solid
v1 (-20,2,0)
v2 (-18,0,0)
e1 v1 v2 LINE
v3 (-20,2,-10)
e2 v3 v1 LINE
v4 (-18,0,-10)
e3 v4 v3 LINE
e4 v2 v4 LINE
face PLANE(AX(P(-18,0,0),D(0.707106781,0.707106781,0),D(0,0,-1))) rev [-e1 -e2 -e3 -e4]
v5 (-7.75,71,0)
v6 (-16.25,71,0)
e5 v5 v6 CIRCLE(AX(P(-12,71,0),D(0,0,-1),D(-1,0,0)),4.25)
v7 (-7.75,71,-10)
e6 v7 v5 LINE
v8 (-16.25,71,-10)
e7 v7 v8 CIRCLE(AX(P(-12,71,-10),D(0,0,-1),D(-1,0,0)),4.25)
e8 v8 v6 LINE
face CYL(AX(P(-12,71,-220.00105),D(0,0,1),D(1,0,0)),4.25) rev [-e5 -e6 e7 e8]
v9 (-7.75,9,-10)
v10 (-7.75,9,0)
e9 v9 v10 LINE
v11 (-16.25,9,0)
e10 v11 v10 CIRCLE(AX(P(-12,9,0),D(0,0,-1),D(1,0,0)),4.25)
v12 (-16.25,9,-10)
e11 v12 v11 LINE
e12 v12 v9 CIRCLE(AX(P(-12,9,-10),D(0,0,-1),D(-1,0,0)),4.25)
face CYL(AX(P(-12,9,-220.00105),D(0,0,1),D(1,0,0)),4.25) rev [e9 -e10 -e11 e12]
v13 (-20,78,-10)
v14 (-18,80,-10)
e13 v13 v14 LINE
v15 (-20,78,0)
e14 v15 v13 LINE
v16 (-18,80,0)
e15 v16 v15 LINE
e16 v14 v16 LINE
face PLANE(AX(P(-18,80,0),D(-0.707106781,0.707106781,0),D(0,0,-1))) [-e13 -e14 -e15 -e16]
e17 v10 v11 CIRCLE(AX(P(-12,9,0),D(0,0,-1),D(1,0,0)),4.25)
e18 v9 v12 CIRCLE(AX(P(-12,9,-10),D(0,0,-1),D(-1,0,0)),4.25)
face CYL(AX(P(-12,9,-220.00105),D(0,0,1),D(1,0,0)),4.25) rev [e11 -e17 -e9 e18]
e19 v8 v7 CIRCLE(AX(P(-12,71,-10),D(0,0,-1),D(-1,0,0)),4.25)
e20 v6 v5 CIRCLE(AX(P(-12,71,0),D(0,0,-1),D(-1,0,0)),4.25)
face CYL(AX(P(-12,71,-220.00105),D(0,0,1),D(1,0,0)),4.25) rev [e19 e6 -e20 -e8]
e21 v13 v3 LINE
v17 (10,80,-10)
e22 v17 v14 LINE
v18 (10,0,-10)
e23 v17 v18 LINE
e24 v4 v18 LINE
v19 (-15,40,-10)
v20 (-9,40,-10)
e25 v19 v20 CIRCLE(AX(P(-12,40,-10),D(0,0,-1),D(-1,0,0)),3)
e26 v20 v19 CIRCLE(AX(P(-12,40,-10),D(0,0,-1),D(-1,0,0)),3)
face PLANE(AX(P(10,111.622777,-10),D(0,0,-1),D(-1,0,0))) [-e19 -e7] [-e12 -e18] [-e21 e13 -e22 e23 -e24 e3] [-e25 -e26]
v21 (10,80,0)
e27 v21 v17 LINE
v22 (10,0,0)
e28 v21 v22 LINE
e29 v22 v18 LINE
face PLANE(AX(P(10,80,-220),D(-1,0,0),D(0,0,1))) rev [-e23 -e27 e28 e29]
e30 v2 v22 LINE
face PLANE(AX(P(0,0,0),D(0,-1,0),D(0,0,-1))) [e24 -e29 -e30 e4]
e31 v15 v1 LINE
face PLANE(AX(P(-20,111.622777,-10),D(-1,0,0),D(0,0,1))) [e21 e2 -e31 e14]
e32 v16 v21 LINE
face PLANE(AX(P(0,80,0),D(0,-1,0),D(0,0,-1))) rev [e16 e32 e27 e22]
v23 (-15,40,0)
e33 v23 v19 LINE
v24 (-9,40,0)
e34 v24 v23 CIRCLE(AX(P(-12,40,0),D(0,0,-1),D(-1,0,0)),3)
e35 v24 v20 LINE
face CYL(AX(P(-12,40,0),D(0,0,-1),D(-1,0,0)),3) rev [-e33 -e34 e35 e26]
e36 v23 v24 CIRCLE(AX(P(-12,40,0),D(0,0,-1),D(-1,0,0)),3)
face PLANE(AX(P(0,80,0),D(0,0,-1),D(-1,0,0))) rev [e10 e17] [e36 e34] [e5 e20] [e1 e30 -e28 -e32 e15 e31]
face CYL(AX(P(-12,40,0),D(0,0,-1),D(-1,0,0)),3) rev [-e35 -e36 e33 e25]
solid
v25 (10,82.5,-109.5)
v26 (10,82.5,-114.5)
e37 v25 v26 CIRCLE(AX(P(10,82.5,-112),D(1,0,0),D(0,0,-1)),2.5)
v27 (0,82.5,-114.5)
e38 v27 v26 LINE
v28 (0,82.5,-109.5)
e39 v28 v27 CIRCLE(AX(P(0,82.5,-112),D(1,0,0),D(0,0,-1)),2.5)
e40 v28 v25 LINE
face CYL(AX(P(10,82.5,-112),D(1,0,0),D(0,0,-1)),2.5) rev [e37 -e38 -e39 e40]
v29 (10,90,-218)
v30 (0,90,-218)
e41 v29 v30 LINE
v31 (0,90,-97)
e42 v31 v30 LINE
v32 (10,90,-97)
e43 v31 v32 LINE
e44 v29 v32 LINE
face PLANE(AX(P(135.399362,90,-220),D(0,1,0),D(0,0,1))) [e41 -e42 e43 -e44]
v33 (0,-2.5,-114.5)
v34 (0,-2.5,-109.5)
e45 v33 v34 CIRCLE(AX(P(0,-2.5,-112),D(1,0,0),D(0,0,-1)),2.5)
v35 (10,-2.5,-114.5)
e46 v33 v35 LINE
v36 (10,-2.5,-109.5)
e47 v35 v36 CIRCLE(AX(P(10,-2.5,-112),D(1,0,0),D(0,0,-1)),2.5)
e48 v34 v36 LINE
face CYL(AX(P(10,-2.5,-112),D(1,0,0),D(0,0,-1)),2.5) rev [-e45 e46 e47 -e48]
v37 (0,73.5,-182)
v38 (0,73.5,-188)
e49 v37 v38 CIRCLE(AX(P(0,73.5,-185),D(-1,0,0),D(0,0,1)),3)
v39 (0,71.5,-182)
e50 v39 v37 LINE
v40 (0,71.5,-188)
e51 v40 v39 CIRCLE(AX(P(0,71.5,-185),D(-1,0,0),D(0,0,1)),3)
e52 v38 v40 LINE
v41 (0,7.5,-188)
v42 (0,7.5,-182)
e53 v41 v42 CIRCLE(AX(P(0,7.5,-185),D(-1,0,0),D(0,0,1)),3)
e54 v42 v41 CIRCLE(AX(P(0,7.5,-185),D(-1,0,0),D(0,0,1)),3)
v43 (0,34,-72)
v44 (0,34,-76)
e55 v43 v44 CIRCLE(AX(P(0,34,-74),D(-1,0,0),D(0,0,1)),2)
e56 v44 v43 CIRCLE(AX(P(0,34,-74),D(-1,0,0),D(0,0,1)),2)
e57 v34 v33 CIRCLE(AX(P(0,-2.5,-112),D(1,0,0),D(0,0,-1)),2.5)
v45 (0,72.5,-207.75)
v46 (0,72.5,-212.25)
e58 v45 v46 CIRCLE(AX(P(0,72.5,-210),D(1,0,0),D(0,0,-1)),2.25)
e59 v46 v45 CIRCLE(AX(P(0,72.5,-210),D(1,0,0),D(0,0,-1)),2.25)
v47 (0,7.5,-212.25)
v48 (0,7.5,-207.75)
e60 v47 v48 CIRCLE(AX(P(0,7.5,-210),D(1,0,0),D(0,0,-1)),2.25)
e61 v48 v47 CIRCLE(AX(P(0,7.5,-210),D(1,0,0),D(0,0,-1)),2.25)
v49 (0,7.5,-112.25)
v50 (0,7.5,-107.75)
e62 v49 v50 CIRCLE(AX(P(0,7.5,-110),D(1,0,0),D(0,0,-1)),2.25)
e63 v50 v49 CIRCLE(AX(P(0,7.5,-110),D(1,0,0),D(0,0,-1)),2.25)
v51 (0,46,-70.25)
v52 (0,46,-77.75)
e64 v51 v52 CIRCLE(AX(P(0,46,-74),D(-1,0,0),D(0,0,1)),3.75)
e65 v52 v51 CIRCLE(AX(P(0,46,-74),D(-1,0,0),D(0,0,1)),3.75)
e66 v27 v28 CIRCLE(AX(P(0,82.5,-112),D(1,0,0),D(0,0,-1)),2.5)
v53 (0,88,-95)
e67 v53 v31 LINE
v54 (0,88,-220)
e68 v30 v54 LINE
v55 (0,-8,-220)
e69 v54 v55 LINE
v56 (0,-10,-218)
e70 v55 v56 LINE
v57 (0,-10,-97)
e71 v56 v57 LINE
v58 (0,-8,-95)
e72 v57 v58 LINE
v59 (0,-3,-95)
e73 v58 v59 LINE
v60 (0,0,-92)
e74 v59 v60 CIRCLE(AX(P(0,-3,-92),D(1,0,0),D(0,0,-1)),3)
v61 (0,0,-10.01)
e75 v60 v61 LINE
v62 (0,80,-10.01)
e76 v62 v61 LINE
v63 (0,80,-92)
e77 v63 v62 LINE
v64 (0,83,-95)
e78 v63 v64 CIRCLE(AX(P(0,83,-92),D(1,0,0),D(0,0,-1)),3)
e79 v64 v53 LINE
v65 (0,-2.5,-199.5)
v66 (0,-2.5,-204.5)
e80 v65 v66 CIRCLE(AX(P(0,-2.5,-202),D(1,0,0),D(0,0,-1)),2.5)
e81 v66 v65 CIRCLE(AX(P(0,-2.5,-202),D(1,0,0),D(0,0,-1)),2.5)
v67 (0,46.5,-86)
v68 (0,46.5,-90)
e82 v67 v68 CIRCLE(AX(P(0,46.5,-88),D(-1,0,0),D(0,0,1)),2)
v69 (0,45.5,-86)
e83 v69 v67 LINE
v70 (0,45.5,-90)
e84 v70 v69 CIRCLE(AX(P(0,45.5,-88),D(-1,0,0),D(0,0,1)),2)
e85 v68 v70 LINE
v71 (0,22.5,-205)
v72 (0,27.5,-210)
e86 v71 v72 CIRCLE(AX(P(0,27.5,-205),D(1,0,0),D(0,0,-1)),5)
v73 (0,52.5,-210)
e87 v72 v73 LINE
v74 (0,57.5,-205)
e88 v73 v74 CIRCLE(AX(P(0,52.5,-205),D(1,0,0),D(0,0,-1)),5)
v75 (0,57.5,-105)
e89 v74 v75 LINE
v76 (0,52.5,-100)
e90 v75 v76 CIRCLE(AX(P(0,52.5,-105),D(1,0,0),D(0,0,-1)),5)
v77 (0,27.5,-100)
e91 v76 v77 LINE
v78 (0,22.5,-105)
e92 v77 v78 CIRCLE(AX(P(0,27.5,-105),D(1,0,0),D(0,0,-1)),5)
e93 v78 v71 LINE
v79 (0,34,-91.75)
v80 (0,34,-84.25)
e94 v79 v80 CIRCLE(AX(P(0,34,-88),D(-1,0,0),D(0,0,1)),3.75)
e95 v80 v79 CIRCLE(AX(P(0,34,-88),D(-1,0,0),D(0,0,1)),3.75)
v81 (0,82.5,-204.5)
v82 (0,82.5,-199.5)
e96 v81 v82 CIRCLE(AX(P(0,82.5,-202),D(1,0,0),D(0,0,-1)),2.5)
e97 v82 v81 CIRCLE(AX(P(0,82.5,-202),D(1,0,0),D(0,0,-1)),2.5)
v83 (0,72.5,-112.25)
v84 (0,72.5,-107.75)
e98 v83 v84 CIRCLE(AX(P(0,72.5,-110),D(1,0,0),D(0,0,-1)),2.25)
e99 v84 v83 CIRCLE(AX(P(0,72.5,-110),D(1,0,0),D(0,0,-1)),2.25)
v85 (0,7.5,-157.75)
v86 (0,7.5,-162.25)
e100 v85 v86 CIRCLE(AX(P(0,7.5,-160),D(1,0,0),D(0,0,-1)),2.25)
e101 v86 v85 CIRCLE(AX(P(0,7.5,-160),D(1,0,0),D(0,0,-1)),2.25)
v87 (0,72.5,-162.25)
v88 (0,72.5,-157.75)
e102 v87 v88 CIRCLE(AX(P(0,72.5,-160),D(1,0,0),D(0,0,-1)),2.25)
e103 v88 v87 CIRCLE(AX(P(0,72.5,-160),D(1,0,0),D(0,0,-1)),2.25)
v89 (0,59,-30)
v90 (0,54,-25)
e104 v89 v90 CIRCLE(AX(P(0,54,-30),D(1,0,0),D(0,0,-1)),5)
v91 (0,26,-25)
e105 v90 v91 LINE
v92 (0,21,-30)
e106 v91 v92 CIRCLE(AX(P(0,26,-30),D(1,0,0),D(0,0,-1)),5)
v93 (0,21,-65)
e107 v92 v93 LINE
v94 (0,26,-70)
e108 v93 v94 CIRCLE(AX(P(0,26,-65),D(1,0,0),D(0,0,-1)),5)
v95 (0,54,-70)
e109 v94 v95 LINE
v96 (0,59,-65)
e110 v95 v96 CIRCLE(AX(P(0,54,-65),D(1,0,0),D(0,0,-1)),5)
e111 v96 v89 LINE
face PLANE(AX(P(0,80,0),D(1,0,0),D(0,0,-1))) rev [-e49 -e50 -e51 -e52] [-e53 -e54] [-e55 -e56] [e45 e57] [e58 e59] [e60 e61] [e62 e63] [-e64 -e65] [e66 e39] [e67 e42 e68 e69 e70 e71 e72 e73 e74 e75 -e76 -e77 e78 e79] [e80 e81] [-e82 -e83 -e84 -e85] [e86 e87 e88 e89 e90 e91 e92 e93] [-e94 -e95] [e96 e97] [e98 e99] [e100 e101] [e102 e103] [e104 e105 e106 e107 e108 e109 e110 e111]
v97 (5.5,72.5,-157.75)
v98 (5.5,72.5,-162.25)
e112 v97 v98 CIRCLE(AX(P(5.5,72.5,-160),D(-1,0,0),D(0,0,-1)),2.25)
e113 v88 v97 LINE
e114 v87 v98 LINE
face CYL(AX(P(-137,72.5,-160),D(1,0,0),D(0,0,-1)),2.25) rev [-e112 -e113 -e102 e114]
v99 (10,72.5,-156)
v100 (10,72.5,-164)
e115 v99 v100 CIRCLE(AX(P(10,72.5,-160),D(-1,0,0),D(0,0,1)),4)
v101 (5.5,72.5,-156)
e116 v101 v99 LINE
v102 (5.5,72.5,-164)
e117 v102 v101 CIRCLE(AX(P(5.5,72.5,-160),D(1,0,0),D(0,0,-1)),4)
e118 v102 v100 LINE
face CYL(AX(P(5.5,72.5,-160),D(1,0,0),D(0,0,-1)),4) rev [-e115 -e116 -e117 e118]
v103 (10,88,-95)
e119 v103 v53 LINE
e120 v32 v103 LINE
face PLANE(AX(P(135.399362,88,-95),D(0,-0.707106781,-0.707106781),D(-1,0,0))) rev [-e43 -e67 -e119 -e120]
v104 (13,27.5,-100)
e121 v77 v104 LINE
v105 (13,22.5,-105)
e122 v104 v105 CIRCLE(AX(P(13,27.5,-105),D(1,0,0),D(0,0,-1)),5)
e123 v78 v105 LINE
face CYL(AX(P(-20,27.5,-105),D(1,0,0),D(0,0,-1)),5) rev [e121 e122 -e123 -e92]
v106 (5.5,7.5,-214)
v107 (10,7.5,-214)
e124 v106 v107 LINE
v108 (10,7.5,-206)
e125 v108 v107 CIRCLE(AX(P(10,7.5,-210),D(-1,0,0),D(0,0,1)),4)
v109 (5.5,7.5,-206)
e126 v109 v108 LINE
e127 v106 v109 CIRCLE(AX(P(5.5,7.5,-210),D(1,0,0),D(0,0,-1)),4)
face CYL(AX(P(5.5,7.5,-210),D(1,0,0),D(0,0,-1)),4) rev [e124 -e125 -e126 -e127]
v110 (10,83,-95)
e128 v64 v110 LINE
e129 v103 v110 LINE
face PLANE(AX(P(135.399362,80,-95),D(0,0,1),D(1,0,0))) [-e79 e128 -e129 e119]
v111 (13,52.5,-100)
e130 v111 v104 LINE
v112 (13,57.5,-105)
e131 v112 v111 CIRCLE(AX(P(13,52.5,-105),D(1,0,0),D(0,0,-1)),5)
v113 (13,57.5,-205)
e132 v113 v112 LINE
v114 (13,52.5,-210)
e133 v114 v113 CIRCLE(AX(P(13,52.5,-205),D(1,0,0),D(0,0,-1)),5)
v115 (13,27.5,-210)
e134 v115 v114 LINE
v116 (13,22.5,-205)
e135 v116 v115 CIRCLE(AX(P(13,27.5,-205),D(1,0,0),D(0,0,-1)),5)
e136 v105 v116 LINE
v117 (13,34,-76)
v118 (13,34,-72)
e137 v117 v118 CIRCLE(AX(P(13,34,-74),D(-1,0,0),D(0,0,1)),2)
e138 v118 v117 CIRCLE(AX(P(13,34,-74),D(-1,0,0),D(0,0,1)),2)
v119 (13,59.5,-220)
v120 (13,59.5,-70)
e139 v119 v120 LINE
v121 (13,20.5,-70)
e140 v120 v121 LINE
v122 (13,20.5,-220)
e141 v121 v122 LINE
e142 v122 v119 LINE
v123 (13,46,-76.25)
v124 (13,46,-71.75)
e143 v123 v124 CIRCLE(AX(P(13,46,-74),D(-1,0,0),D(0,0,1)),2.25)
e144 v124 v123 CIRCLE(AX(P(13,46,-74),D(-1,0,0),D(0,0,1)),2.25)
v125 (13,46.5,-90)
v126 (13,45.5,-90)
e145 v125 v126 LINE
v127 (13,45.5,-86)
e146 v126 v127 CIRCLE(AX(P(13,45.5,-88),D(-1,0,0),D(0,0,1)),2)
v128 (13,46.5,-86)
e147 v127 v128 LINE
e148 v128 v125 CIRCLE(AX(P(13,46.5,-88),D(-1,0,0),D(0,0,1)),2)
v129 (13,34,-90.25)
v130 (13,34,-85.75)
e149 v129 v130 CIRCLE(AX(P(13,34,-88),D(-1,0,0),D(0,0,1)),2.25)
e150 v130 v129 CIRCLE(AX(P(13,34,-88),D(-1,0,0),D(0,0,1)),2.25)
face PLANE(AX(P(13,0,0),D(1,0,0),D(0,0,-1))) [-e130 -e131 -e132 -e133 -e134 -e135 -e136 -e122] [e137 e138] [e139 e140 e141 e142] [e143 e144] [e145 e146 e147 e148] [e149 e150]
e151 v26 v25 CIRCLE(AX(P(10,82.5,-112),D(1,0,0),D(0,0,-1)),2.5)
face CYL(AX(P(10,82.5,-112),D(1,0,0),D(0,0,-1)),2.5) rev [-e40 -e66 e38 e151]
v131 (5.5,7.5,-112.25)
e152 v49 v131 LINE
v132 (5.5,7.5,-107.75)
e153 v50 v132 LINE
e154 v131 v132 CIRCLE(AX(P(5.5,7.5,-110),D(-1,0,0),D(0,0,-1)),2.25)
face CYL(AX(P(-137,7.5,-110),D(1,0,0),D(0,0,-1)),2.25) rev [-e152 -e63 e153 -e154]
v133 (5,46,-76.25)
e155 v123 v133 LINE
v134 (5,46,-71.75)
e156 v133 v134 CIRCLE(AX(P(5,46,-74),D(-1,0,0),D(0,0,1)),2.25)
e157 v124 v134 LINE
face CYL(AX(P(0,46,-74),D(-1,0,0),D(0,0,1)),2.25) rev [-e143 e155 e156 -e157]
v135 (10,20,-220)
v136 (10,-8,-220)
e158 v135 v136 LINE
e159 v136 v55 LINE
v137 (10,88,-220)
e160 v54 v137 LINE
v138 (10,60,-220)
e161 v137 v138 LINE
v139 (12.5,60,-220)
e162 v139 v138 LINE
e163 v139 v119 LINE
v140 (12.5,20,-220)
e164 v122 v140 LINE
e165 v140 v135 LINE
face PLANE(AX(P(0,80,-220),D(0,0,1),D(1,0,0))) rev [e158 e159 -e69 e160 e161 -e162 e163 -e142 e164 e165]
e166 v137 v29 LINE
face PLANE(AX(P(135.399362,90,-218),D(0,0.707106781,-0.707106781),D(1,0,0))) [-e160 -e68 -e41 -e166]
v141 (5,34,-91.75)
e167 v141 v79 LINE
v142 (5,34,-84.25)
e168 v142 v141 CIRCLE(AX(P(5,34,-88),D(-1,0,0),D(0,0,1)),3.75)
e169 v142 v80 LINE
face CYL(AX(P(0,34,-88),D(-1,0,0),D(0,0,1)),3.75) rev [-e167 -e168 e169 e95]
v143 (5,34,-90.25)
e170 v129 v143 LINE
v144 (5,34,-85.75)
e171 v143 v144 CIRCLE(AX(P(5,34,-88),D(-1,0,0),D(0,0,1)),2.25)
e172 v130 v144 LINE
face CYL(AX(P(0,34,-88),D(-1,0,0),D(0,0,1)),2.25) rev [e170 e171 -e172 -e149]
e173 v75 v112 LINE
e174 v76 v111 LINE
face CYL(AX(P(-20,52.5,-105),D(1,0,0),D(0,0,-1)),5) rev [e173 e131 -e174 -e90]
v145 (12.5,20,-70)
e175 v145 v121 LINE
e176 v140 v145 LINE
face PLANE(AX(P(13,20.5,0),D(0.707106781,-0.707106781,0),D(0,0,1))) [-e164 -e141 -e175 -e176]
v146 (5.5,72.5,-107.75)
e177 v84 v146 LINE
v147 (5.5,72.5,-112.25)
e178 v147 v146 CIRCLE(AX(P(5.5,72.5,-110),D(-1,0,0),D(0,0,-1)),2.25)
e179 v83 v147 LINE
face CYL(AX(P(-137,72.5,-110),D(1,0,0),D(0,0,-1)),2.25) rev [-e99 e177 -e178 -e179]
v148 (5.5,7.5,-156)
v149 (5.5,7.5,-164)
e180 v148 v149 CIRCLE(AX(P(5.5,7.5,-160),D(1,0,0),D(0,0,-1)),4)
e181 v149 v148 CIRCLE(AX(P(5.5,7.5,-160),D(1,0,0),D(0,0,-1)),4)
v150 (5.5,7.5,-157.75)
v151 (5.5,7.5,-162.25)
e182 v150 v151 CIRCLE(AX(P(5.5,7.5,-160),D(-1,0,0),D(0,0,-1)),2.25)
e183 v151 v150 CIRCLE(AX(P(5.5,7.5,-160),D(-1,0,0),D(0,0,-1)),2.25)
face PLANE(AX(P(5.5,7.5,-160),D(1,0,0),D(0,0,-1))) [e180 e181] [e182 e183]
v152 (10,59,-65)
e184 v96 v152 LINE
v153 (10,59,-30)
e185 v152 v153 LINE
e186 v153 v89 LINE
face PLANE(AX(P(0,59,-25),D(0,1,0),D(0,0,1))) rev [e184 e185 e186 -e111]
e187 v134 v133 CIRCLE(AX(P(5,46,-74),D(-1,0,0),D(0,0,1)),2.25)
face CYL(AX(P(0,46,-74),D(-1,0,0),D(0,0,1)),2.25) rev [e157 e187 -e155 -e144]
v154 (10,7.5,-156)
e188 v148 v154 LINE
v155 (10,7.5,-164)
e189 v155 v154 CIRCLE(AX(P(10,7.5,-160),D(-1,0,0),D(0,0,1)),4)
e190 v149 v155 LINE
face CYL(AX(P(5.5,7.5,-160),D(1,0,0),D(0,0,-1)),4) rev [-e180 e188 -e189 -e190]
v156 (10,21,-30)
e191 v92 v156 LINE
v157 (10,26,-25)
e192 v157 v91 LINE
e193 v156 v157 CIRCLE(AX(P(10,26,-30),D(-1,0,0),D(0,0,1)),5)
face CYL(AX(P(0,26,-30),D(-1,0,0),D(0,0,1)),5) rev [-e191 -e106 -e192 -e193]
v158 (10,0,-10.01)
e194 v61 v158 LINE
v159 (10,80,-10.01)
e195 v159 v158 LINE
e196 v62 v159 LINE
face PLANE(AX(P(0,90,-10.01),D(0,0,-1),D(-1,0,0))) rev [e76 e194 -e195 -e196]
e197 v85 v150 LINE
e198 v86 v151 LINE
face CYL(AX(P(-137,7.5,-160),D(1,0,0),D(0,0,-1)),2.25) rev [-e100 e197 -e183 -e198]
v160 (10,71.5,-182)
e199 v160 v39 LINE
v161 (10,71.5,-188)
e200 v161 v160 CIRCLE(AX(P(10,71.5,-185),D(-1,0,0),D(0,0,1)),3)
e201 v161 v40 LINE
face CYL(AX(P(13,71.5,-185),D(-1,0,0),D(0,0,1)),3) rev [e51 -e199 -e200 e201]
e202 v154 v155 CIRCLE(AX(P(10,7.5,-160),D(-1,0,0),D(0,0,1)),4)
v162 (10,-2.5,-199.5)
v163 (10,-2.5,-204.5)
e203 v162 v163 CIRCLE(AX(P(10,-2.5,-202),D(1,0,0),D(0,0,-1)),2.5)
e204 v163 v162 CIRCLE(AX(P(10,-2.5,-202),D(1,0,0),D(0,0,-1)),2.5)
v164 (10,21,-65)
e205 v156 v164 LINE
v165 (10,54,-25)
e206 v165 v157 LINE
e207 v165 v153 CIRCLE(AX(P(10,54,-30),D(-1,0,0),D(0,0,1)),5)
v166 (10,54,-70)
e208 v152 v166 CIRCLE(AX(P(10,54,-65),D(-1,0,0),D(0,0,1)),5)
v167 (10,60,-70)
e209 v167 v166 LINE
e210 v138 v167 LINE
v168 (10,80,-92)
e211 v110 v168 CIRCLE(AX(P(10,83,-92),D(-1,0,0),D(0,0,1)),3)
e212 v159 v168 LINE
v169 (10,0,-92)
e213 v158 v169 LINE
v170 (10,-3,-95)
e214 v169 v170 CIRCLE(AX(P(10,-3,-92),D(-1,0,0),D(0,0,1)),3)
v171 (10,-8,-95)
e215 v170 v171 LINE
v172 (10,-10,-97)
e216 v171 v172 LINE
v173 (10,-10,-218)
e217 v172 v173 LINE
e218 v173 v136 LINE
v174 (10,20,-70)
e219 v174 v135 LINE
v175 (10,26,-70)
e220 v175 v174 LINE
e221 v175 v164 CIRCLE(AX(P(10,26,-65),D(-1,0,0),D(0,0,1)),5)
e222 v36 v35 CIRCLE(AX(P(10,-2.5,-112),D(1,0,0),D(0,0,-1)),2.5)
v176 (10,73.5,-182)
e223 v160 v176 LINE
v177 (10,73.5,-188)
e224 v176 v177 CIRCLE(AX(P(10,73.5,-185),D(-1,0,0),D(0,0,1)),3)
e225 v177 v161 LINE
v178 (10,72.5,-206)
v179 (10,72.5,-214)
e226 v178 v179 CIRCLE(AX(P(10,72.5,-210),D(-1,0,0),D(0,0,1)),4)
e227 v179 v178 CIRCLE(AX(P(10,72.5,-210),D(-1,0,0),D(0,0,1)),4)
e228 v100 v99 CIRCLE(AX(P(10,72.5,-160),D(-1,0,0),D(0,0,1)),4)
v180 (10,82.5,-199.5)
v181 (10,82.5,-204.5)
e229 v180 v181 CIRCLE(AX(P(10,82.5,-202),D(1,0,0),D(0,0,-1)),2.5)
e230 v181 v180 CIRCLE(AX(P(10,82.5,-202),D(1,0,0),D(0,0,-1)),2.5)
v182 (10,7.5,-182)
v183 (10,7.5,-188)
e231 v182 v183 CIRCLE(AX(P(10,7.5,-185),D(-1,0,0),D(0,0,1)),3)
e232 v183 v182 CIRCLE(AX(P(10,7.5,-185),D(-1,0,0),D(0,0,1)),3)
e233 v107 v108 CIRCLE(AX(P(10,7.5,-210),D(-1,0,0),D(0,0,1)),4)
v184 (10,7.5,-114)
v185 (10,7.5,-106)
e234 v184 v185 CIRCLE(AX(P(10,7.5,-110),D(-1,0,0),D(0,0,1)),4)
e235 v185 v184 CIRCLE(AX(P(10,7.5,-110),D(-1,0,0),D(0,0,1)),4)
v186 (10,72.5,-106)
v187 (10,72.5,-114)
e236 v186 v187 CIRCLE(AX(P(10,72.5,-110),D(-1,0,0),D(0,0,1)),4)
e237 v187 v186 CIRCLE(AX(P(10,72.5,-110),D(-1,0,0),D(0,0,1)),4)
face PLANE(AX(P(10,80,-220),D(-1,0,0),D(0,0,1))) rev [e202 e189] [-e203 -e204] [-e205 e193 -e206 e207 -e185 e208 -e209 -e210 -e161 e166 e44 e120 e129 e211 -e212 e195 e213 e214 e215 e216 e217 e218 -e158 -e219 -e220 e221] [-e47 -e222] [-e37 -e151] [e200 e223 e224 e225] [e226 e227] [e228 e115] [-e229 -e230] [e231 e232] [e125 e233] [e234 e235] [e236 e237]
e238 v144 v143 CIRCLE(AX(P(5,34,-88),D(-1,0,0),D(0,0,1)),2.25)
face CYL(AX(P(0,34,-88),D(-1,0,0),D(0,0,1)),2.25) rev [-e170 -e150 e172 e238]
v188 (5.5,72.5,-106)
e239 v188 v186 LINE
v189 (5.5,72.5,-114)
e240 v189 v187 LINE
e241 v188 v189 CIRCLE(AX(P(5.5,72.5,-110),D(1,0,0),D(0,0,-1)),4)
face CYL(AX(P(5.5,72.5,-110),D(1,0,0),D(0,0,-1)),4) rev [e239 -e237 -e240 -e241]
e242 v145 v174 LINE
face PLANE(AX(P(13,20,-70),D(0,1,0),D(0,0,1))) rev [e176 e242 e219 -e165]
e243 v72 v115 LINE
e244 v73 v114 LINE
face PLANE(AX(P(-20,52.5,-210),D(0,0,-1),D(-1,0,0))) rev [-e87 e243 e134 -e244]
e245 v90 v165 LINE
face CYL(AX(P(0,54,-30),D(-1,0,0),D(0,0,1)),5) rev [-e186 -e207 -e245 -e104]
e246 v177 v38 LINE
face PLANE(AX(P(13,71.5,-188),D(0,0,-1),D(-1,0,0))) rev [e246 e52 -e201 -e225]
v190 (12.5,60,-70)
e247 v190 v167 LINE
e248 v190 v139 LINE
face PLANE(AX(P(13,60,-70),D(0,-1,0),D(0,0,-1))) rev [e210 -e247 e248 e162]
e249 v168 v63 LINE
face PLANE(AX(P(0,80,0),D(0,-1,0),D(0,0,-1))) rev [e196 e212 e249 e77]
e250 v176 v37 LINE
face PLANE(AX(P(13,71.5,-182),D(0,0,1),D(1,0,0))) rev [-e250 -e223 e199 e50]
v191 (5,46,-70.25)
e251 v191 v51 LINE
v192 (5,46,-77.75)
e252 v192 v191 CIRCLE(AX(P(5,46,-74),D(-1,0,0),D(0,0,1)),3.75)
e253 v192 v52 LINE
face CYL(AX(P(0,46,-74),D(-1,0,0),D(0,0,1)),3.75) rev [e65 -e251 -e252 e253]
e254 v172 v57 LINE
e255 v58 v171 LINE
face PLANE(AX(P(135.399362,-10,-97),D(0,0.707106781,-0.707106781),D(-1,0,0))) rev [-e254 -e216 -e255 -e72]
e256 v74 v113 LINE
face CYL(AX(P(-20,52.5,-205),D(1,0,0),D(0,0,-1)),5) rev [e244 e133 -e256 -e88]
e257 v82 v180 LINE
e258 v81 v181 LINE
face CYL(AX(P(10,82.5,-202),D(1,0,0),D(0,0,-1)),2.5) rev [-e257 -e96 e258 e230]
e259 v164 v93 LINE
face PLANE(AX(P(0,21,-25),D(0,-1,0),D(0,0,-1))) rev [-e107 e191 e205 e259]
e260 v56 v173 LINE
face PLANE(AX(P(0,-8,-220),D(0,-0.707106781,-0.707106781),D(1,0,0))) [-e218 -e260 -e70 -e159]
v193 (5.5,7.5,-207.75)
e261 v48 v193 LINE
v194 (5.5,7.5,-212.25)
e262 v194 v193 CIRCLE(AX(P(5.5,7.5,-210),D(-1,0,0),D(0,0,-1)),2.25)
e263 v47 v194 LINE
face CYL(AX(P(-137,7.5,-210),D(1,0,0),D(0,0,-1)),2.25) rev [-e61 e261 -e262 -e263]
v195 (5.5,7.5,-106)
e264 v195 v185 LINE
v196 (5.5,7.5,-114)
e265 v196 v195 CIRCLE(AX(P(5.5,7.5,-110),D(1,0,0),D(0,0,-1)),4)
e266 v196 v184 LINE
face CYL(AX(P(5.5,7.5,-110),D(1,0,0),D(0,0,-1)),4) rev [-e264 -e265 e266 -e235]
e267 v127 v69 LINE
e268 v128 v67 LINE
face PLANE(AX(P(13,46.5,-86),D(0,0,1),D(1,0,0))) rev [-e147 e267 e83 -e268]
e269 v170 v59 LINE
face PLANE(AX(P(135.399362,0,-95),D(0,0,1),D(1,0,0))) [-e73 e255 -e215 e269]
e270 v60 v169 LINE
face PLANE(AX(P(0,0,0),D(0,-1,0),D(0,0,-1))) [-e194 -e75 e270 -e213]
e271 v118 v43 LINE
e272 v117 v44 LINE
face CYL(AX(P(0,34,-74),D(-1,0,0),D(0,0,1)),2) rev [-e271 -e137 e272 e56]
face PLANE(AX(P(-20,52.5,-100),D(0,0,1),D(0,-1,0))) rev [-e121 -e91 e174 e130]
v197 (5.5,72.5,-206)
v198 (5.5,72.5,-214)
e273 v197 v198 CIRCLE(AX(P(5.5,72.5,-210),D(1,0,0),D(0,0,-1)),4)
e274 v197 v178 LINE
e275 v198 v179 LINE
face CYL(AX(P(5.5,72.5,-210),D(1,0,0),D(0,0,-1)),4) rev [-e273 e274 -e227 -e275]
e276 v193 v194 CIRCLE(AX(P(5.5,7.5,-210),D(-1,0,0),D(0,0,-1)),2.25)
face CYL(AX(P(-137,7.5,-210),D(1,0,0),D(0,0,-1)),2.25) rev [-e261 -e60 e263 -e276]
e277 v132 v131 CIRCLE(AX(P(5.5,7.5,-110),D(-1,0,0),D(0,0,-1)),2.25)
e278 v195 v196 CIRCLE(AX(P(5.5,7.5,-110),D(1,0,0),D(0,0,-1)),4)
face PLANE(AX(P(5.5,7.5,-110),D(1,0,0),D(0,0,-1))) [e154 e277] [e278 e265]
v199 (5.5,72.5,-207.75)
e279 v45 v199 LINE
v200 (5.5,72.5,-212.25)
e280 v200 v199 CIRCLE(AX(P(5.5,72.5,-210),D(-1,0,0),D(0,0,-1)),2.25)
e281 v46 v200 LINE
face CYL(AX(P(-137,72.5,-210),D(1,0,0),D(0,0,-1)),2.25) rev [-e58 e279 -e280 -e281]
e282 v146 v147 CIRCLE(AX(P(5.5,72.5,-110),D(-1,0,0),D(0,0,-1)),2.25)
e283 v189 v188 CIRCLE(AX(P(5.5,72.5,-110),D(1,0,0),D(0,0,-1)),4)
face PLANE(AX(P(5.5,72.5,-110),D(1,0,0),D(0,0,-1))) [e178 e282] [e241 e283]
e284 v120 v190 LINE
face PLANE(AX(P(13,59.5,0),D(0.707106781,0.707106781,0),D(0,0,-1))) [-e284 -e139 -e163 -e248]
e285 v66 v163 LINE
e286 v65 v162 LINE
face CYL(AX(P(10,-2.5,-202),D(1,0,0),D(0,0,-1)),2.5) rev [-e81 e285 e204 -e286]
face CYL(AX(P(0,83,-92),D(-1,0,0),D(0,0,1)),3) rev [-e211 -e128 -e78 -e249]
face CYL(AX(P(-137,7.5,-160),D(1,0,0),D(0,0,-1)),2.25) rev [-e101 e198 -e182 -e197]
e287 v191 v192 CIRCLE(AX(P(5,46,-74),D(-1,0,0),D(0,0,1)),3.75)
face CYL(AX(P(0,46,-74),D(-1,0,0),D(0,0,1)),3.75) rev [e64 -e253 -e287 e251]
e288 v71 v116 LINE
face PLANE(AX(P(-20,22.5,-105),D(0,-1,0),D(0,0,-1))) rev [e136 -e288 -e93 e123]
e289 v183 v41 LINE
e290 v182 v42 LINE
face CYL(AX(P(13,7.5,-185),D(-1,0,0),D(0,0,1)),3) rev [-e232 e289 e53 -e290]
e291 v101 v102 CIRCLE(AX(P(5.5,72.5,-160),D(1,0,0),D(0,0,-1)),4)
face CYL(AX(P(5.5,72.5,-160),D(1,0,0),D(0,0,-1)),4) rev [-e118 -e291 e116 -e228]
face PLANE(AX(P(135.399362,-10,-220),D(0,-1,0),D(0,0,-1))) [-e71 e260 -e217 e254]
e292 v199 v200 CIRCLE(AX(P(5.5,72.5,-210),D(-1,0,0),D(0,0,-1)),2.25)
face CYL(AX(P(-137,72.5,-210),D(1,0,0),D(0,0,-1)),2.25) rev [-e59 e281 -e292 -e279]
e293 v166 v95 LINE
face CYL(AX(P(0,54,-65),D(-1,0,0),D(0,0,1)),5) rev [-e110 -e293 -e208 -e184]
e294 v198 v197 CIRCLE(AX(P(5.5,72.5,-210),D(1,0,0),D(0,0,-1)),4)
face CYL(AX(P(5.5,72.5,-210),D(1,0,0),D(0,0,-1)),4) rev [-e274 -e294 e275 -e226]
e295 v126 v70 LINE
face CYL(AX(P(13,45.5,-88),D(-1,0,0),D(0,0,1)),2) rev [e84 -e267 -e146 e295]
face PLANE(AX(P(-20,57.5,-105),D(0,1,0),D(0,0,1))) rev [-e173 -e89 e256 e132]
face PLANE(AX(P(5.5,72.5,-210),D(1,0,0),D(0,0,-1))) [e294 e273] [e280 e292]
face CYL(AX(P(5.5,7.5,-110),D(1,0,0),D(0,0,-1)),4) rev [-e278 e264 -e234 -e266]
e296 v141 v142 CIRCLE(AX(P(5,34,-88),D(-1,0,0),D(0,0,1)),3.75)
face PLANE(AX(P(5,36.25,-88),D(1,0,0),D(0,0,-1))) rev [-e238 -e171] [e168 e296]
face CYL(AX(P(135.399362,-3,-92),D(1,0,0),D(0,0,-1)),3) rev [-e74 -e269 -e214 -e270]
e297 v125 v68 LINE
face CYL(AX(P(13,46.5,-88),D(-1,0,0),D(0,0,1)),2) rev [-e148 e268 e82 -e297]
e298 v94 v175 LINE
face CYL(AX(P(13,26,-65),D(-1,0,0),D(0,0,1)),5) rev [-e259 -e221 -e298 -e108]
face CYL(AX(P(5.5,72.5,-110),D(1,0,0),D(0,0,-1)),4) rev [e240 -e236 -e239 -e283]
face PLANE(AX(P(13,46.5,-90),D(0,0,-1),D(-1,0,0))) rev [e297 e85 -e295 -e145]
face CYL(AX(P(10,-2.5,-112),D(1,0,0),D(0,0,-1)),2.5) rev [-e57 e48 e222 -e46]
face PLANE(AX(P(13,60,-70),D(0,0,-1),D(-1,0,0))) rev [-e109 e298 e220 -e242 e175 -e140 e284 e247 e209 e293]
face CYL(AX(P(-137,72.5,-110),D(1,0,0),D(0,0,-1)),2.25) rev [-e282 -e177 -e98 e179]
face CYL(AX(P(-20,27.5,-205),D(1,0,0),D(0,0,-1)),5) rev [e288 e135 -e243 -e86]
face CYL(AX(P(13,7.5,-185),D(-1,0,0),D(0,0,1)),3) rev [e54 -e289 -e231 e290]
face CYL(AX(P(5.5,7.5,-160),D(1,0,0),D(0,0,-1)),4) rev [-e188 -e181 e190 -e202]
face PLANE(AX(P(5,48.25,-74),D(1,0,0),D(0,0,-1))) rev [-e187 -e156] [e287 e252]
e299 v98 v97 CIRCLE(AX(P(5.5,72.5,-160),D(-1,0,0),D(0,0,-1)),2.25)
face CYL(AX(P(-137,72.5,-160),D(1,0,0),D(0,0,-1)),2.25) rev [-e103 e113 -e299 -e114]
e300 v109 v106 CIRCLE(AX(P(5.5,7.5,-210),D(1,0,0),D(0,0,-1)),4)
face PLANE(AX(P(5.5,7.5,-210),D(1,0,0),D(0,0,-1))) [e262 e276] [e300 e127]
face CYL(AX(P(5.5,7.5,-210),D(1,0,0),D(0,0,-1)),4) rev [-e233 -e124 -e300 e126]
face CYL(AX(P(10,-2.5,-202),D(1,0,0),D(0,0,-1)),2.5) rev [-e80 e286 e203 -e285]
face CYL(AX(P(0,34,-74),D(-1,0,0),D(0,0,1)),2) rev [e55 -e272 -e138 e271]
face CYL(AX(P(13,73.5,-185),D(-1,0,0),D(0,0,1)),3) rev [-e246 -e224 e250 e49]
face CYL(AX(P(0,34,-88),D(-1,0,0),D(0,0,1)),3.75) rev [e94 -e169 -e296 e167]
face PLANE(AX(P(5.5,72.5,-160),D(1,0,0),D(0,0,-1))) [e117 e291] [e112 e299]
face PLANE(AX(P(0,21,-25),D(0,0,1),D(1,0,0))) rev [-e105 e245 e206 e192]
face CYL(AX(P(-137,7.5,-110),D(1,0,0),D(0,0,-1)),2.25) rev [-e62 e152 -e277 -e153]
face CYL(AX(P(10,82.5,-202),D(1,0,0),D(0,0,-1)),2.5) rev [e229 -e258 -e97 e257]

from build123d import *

# Parameters (mm, degrees)
BOSS_EXTRUDE1_DEPTH                                  = 80
CHAMFER1_SIZE                                        = 10
SKETCH2_W                                            = 30
SKETCH2_H                                            = 10
BOSS_EXTRUDE2_DEPTH                                  = 80
SKETCH3_W                                            = 10
SKETCH3_H                                            = 8
CUT_EXTRUDE1_DEPTH                                   = 96
SKETCH4_W                                            = 150
SKETCH4_H                                            = 40
BOSS_EXTRUDE3_DEPTH                                  = 3
CUT_EXTRUDE2_REACH                                   = 236.947
SKETCH5_R                                            = 4.25
CHAMFER5_SIZE                                        = 0.5
SKETCH13_R                                           = 2.25
CUT_EXTRUDE7_DEPTH                                   = 150
SKETCH14_R                                           = 4
CUT_EXTRUDE8_DEPTH                                   = 7.5
SKETCH15_W                                           = 125
SKETCH15_H                                           = 10
BOSS_EXTRUDE5_DEPTH                                  = 10
SKETCH9_R                                            = 1
CUT_EXTRUDE4_DEPTH                                   = 25
M6_TAPPED_HOLE1_D                                    = 5
SKETCH18_W                                           = 45
SKETCH18_H                                           = 38
CUT_EXTRUDE10_DEPTH                                  = 10
FILLET2_R                                            = 5
FILLET3_R                                            = 3
CHAMFER6_SIZE                                        = 2
HOLE_SIZE_PER_SOCKET_HEAD_CAP_SCREW_TYPE_D           = 4.5
HOLE_SIZE_PER_SOCKET_HEAD_CAP_SCREW_TYPE_CBORE_D     = 7.5
HOLE_SIZE_PER_SOCKET_HEAD_CAP_SCREW_TYPE_CBORE_DEPTH = 5
F_4_0_4_DIAMETER_HOLE1_D                             = 4
CUT_EXTRUDE11_DEPTH                                  = 240.977082239
SKETCH24_R                                           = 3
CUT_EXTRUDE12_DEPTH                                  = 239.537208838
SKETCH25_W                                           = 10
SKETCH25_H                                           = 0.01
CUT_EXTRUDE13_DEPTH                                  = 239.537208838
SKETCH26_R                                           = 3
CUT_EXTRUDE14_DEPTH                                  = 230.346898824
CUT_EXTRUDE15_DEPTH                                  = 239.537208838


with BuildPart() as part:
    # Sketch1 → Boss-Extrude1 (new body)
    with BuildSketch(Plane(origin=(0, 0, 0), x_dir=(1, 0, 0), z_dir=(0, 1, 0))):
        Polygon((0, 0), (20, 0), (20, 8), (10, 8), (10, 220), (0, 220), align=None)
    extrude(amount=BOSS_EXTRUDE1_DEPTH)

    # Chamfer1
    chamfer1_edges = [part.edges().sort_by_distance(p)[0] for p in [
        (20, 80, -4),
        (20, 0, -4),
    ]]
    chamfer(chamfer1_edges, length=CHAMFER1_SIZE)

    # Sketch2 → Boss-Extrude2 (add)
    with BuildSketch(Plane.XZ):
        with Locations((-5, -5)):
            Rectangle(SKETCH2_W, SKETCH2_H)
    extrude(amount=-BOSS_EXTRUDE2_DEPTH)

    # Sketch3 → Cut-Extrude1 (cut)
    with BuildSketch(Plane.XZ):
        with Locations((15, -4)):
            Rectangle(SKETCH3_W, SKETCH3_H)
    extrude(amount=-CUT_EXTRUDE1_DEPTH, mode=Mode.SUBTRACT)

    # Sketch4 → Boss-Extrude3 (add)
    with BuildSketch(Plane(origin=(10, 0, 0), x_dir=(0, 0, -1), z_dir=(1, 0, 0))):
        with Locations((145, 40)):
            Rectangle(SKETCH4_W, SKETCH4_H)
    extrude(amount=BOSS_EXTRUDE3_DEPTH)

    # Sketch5 → Cut-Extrude2 (cut, up to next)
    with BuildSketch(Plane(origin=(0, 0, 0), x_dir=(-1, 0, 0), z_dir=(0, 0, -1)), mode=Mode.PRIVATE) as cut_extrude2_sk1:
        with Locations((12, 71)):
            Circle(SKETCH5_R)
    cut_extrude2_tool1 = extrude(cut_extrude2_sk1.sketch, amount=CUT_EXTRUDE2_REACH, mode=Mode.PRIVATE) & part.part
    # Sketch5 → Cut-Extrude2 (cut, up to next)
    with BuildSketch(Plane(origin=(0, 0, 0), x_dir=(-1, 0, 0), z_dir=(0, 0, -1)), mode=Mode.PRIVATE) as cut_extrude2_sk2:
        with Locations(Location((12, 9, 0), (0, 0, 180))):
            Circle(SKETCH5_R)
    cut_extrude2_tool2 = extrude(cut_extrude2_sk2.sketch, amount=CUT_EXTRUDE2_REACH, mode=Mode.PRIVATE) & part.part
    add(cut_extrude2_tool1.solids().sort_by_distance((-12, 71, 0))[0], mode=Mode.SUBTRACT)
    add(cut_extrude2_tool2.solids().sort_by_distance((-12, 9, 0))[0], mode=Mode.SUBTRACT)

    # Chamfer5
    chamfer5_edges = [part.edges().sort_by_distance(p)[0] for p in [
        (13, 60, -145),
        (13, 20, -145),
    ]]
    chamfer(chamfer5_edges, length=CHAMFER5_SIZE)

    # Sketch13 → Cut-Extrude7 (cut)
    with BuildSketch(Plane(origin=(13, 0, 0), x_dir=(0, 0, -1), z_dir=(1, 0, 0))):
        with Locations((210, 72.5)):
            Circle(SKETCH13_R)
        with Locations((110, 72.5)):
            Circle(SKETCH13_R)
        with Locations((210, 7.5)):
            Circle(SKETCH13_R)
        with Locations((110, 7.5)):
            Circle(SKETCH13_R)
        with Locations((160, 72.5)):
            Circle(SKETCH13_R)
        with Locations((160, 7.5)):
            Circle(SKETCH13_R)
    extrude(amount=-CUT_EXTRUDE7_DEPTH, mode=Mode.SUBTRACT)

    # Sketch14 → Cut-Extrude8 (cut)
    with BuildSketch(Plane(origin=(13, 0, 0), x_dir=(0, 0, -1), z_dir=(1, 0, 0))):
        with Locations((110, 72.5)):
            Circle(SKETCH14_R)
        with Locations((110, 7.5)):
            Circle(SKETCH14_R)
        with Locations((210, 7.5)):
            Circle(SKETCH14_R)
        with Locations((210, 72.5)):
            Circle(SKETCH14_R)
        with Locations((160, 72.5)):
            Circle(SKETCH14_R)
        with Locations((160, 7.5)):
            Circle(SKETCH14_R)
    extrude(amount=-CUT_EXTRUDE8_DEPTH, mode=Mode.SUBTRACT)

    # Sketch15 → Boss-Extrude5 (add)
    with BuildSketch(Plane.ZY):
        with Locations((-157.5, -5)):
            Rectangle(SKETCH15_W, SKETCH15_H)
        with Locations((-157.5, 85)):
            Rectangle(SKETCH15_W, SKETCH15_H)
    extrude(amount=-BOSS_EXTRUDE5_DEPTH)

    # Sketch9 → Cut-Extrude4 (cut)
    with BuildSketch(Plane(origin=(10, 0, 0), x_dir=(0, 0, -1), z_dir=(1, 0, 0))):
        with Locations((202, 82.5)):
            Circle(SKETCH9_R)
        with Locations((112, 82.5)):
            Circle(SKETCH9_R)
        with Locations((112, -2.5)):
            Circle(SKETCH9_R)
        with Locations((202, -2.5)):
            Circle(SKETCH9_R)
    extrude(amount=-CUT_EXTRUDE4_DEPTH, mode=Mode.SUBTRACT)

    # M6 Tapped Hole1 (through all)
    with Locations(Plane(origin=(10, 82.5, -202), x_dir=(0, 0, 1), z_dir=(1, 0, 0))):
        with Locations((0, 0), (90, 0), (90, 85), (0, 85)):
            Hole(M6_TAPPED_HOLE1_D / 2)

    # Sketch18 → Cut-Extrude10 (cut)
    with BuildSketch(Plane(origin=(10, 0, 0), x_dir=(0, 0, -1), z_dir=(1, 0, 0))):
        with Locations((47.5, 40)):
            Rectangle(SKETCH18_W, SKETCH18_H)
    extrude(amount=-CUT_EXTRUDE10_DEPTH, mode=Mode.SUBTRACT)

    # Fillet2
    fillet2_edges = [part.edges().sort_by_distance(p)[0] for p in [
        (5, 59, -70),
        (5, 21, -70),
        (5, 21, -25),
        (5, 59, -25),
    ]]
    fillet(fillet2_edges, radius=FILLET2_R)

    # Fillet3
    fillet3_edges = [part.edges().sort_by_distance(p)[0] for p in [
        (5, 80, -95),
        (5, 0, -95),
    ]]
    fillet(fillet3_edges, radius=FILLET3_R)

    # Chamfer6
    chamfer6_edges = [part.edges().sort_by_distance(p)[0] for p in [
        (5, 90, -220),
        (5, -10, -220),
        (5, 90, -95),
        (5, -10, -95),
        (-20, 80, -5),
        (-20, 0, -5),
    ]]
    chamfer(chamfer6_edges, length=CHAMFER6_SIZE)

    # Hole size per socket head cap screw type 5 (through all)
    with Locations(Plane.ZY):
        with Locations((-88, 34), (-74, 46)):
            CounterBoreHole(HOLE_SIZE_PER_SOCKET_HEAD_CAP_SCREW_TYPE_D / 2, HOLE_SIZE_PER_SOCKET_HEAD_CAP_SCREW_TYPE_CBORE_D / 2, HOLE_SIZE_PER_SOCKET_HEAD_CAP_SCREW_TYPE_CBORE_DEPTH)

    # Ø4.0 (4) Diameter Hole1 (through all)
    with Locations(Plane.ZY):
        with Locations((-74, 34), (-88, 46)):
            Hole(F_4_0_4_DIAMETER_HOLE1_D / 2)

    # Sketch23 → Cut-Extrude11 (cut, through all)
    with BuildSketch(Plane(origin=(13, 0, 0), x_dir=(0, 0, -1), z_dir=(1, 0, 0))):
        with BuildLine():
            Line((105, 57.5), (205, 57.5))
            ThreePointArc((205, 57.5), (208.535533906, 56.035533906), (210, 52.5))
            Line((210, 52.5), (210, 27.5))
            ThreePointArc((210, 27.5), (208.535533906, 23.964466094), (205, 22.5))
            Line((205, 22.5), (105, 22.5))
            ThreePointArc((105, 22.5), (101.464466094, 23.964466094), (100, 27.5))
            Line((100, 27.5), (100, 52.5))
            ThreePointArc((100, 52.5), (101.464466094, 56.035533906), (105, 57.5))
        make_face()
    extrude(amount=-CUT_EXTRUDE11_DEPTH, mode=Mode.SUBTRACT)

    # Sketch24 → Cut-Extrude12 (cut, through all)
    with BuildSketch(Plane.ZY):
        with Locations((-185, 7.5)):
            Circle(SKETCH24_R)
        with BuildLine():
            Line((-188, 71.5), (-188, 73.5))
            ThreePointArc((-188, 73.5), (-185, 76.5), (-182, 73.5))
            Line((-182, 73.5), (-182, 71.5))
            ThreePointArc((-182, 71.5), (-185, 68.5), (-188, 71.5))
        make_face()
    extrude(amount=-CUT_EXTRUDE12_DEPTH, mode=Mode.SUBTRACT)

    # Sketch25 → Cut-Extrude13 (cut, through all)
    with BuildSketch(Plane.XZ):
        with Locations((5, -10.005)):
            Rectangle(SKETCH25_W, SKETCH25_H)
    extrude(amount=-CUT_EXTRUDE13_DEPTH, mode=Mode.SUBTRACT)


with BuildPart() as cut_extrude13_piece_1:
    # of the separate pieces the step leaves, piece 1, a body of its own (cut_extrude13_pieces)
    add(part.part.solids().sort_by_distance((10, -8, -95))[0])

    # Sketch28 → Cut-Extrude15 (cut, through all)
    with BuildSketch(Plane.ZY):
        with BuildLine():
            Line((-86, 46.5), (-86, 45.5))
            ThreePointArc((-86, 45.5), (-88, 43.5), (-90, 45.5))
            Line((-90, 45.5), (-90, 46.5))
            ThreePointArc((-90, 46.5), (-88, 48.5), (-86, 46.5))
        make_face()
    extrude(amount=-CUT_EXTRUDE15_DEPTH, mode=Mode.SUBTRACT)


with BuildPart() as cut_extrude13_piece_2:
    # of the separate pieces the step leaves, piece 2, a body of its own (cut_extrude13_pieces)
    add(part.part.solids().sort_by_distance((10, 0, -10))[0])

    # Sketch26 → Cut-Extrude14 (cut, through all)
    with BuildSketch(Plane(origin=(0, 0, -10), x_dir=(-1, 0, 0), z_dir=(0, 0, -1))):
        with Locations((12, 40)):
            Circle(SKETCH26_R)
    extrude(amount=-CUT_EXTRUDE14_DEPTH, mode=Mode.SUBTRACT)


solid = Compound([cut_extrude13_piece_1.part, cut_extrude13_piece_2.part])
